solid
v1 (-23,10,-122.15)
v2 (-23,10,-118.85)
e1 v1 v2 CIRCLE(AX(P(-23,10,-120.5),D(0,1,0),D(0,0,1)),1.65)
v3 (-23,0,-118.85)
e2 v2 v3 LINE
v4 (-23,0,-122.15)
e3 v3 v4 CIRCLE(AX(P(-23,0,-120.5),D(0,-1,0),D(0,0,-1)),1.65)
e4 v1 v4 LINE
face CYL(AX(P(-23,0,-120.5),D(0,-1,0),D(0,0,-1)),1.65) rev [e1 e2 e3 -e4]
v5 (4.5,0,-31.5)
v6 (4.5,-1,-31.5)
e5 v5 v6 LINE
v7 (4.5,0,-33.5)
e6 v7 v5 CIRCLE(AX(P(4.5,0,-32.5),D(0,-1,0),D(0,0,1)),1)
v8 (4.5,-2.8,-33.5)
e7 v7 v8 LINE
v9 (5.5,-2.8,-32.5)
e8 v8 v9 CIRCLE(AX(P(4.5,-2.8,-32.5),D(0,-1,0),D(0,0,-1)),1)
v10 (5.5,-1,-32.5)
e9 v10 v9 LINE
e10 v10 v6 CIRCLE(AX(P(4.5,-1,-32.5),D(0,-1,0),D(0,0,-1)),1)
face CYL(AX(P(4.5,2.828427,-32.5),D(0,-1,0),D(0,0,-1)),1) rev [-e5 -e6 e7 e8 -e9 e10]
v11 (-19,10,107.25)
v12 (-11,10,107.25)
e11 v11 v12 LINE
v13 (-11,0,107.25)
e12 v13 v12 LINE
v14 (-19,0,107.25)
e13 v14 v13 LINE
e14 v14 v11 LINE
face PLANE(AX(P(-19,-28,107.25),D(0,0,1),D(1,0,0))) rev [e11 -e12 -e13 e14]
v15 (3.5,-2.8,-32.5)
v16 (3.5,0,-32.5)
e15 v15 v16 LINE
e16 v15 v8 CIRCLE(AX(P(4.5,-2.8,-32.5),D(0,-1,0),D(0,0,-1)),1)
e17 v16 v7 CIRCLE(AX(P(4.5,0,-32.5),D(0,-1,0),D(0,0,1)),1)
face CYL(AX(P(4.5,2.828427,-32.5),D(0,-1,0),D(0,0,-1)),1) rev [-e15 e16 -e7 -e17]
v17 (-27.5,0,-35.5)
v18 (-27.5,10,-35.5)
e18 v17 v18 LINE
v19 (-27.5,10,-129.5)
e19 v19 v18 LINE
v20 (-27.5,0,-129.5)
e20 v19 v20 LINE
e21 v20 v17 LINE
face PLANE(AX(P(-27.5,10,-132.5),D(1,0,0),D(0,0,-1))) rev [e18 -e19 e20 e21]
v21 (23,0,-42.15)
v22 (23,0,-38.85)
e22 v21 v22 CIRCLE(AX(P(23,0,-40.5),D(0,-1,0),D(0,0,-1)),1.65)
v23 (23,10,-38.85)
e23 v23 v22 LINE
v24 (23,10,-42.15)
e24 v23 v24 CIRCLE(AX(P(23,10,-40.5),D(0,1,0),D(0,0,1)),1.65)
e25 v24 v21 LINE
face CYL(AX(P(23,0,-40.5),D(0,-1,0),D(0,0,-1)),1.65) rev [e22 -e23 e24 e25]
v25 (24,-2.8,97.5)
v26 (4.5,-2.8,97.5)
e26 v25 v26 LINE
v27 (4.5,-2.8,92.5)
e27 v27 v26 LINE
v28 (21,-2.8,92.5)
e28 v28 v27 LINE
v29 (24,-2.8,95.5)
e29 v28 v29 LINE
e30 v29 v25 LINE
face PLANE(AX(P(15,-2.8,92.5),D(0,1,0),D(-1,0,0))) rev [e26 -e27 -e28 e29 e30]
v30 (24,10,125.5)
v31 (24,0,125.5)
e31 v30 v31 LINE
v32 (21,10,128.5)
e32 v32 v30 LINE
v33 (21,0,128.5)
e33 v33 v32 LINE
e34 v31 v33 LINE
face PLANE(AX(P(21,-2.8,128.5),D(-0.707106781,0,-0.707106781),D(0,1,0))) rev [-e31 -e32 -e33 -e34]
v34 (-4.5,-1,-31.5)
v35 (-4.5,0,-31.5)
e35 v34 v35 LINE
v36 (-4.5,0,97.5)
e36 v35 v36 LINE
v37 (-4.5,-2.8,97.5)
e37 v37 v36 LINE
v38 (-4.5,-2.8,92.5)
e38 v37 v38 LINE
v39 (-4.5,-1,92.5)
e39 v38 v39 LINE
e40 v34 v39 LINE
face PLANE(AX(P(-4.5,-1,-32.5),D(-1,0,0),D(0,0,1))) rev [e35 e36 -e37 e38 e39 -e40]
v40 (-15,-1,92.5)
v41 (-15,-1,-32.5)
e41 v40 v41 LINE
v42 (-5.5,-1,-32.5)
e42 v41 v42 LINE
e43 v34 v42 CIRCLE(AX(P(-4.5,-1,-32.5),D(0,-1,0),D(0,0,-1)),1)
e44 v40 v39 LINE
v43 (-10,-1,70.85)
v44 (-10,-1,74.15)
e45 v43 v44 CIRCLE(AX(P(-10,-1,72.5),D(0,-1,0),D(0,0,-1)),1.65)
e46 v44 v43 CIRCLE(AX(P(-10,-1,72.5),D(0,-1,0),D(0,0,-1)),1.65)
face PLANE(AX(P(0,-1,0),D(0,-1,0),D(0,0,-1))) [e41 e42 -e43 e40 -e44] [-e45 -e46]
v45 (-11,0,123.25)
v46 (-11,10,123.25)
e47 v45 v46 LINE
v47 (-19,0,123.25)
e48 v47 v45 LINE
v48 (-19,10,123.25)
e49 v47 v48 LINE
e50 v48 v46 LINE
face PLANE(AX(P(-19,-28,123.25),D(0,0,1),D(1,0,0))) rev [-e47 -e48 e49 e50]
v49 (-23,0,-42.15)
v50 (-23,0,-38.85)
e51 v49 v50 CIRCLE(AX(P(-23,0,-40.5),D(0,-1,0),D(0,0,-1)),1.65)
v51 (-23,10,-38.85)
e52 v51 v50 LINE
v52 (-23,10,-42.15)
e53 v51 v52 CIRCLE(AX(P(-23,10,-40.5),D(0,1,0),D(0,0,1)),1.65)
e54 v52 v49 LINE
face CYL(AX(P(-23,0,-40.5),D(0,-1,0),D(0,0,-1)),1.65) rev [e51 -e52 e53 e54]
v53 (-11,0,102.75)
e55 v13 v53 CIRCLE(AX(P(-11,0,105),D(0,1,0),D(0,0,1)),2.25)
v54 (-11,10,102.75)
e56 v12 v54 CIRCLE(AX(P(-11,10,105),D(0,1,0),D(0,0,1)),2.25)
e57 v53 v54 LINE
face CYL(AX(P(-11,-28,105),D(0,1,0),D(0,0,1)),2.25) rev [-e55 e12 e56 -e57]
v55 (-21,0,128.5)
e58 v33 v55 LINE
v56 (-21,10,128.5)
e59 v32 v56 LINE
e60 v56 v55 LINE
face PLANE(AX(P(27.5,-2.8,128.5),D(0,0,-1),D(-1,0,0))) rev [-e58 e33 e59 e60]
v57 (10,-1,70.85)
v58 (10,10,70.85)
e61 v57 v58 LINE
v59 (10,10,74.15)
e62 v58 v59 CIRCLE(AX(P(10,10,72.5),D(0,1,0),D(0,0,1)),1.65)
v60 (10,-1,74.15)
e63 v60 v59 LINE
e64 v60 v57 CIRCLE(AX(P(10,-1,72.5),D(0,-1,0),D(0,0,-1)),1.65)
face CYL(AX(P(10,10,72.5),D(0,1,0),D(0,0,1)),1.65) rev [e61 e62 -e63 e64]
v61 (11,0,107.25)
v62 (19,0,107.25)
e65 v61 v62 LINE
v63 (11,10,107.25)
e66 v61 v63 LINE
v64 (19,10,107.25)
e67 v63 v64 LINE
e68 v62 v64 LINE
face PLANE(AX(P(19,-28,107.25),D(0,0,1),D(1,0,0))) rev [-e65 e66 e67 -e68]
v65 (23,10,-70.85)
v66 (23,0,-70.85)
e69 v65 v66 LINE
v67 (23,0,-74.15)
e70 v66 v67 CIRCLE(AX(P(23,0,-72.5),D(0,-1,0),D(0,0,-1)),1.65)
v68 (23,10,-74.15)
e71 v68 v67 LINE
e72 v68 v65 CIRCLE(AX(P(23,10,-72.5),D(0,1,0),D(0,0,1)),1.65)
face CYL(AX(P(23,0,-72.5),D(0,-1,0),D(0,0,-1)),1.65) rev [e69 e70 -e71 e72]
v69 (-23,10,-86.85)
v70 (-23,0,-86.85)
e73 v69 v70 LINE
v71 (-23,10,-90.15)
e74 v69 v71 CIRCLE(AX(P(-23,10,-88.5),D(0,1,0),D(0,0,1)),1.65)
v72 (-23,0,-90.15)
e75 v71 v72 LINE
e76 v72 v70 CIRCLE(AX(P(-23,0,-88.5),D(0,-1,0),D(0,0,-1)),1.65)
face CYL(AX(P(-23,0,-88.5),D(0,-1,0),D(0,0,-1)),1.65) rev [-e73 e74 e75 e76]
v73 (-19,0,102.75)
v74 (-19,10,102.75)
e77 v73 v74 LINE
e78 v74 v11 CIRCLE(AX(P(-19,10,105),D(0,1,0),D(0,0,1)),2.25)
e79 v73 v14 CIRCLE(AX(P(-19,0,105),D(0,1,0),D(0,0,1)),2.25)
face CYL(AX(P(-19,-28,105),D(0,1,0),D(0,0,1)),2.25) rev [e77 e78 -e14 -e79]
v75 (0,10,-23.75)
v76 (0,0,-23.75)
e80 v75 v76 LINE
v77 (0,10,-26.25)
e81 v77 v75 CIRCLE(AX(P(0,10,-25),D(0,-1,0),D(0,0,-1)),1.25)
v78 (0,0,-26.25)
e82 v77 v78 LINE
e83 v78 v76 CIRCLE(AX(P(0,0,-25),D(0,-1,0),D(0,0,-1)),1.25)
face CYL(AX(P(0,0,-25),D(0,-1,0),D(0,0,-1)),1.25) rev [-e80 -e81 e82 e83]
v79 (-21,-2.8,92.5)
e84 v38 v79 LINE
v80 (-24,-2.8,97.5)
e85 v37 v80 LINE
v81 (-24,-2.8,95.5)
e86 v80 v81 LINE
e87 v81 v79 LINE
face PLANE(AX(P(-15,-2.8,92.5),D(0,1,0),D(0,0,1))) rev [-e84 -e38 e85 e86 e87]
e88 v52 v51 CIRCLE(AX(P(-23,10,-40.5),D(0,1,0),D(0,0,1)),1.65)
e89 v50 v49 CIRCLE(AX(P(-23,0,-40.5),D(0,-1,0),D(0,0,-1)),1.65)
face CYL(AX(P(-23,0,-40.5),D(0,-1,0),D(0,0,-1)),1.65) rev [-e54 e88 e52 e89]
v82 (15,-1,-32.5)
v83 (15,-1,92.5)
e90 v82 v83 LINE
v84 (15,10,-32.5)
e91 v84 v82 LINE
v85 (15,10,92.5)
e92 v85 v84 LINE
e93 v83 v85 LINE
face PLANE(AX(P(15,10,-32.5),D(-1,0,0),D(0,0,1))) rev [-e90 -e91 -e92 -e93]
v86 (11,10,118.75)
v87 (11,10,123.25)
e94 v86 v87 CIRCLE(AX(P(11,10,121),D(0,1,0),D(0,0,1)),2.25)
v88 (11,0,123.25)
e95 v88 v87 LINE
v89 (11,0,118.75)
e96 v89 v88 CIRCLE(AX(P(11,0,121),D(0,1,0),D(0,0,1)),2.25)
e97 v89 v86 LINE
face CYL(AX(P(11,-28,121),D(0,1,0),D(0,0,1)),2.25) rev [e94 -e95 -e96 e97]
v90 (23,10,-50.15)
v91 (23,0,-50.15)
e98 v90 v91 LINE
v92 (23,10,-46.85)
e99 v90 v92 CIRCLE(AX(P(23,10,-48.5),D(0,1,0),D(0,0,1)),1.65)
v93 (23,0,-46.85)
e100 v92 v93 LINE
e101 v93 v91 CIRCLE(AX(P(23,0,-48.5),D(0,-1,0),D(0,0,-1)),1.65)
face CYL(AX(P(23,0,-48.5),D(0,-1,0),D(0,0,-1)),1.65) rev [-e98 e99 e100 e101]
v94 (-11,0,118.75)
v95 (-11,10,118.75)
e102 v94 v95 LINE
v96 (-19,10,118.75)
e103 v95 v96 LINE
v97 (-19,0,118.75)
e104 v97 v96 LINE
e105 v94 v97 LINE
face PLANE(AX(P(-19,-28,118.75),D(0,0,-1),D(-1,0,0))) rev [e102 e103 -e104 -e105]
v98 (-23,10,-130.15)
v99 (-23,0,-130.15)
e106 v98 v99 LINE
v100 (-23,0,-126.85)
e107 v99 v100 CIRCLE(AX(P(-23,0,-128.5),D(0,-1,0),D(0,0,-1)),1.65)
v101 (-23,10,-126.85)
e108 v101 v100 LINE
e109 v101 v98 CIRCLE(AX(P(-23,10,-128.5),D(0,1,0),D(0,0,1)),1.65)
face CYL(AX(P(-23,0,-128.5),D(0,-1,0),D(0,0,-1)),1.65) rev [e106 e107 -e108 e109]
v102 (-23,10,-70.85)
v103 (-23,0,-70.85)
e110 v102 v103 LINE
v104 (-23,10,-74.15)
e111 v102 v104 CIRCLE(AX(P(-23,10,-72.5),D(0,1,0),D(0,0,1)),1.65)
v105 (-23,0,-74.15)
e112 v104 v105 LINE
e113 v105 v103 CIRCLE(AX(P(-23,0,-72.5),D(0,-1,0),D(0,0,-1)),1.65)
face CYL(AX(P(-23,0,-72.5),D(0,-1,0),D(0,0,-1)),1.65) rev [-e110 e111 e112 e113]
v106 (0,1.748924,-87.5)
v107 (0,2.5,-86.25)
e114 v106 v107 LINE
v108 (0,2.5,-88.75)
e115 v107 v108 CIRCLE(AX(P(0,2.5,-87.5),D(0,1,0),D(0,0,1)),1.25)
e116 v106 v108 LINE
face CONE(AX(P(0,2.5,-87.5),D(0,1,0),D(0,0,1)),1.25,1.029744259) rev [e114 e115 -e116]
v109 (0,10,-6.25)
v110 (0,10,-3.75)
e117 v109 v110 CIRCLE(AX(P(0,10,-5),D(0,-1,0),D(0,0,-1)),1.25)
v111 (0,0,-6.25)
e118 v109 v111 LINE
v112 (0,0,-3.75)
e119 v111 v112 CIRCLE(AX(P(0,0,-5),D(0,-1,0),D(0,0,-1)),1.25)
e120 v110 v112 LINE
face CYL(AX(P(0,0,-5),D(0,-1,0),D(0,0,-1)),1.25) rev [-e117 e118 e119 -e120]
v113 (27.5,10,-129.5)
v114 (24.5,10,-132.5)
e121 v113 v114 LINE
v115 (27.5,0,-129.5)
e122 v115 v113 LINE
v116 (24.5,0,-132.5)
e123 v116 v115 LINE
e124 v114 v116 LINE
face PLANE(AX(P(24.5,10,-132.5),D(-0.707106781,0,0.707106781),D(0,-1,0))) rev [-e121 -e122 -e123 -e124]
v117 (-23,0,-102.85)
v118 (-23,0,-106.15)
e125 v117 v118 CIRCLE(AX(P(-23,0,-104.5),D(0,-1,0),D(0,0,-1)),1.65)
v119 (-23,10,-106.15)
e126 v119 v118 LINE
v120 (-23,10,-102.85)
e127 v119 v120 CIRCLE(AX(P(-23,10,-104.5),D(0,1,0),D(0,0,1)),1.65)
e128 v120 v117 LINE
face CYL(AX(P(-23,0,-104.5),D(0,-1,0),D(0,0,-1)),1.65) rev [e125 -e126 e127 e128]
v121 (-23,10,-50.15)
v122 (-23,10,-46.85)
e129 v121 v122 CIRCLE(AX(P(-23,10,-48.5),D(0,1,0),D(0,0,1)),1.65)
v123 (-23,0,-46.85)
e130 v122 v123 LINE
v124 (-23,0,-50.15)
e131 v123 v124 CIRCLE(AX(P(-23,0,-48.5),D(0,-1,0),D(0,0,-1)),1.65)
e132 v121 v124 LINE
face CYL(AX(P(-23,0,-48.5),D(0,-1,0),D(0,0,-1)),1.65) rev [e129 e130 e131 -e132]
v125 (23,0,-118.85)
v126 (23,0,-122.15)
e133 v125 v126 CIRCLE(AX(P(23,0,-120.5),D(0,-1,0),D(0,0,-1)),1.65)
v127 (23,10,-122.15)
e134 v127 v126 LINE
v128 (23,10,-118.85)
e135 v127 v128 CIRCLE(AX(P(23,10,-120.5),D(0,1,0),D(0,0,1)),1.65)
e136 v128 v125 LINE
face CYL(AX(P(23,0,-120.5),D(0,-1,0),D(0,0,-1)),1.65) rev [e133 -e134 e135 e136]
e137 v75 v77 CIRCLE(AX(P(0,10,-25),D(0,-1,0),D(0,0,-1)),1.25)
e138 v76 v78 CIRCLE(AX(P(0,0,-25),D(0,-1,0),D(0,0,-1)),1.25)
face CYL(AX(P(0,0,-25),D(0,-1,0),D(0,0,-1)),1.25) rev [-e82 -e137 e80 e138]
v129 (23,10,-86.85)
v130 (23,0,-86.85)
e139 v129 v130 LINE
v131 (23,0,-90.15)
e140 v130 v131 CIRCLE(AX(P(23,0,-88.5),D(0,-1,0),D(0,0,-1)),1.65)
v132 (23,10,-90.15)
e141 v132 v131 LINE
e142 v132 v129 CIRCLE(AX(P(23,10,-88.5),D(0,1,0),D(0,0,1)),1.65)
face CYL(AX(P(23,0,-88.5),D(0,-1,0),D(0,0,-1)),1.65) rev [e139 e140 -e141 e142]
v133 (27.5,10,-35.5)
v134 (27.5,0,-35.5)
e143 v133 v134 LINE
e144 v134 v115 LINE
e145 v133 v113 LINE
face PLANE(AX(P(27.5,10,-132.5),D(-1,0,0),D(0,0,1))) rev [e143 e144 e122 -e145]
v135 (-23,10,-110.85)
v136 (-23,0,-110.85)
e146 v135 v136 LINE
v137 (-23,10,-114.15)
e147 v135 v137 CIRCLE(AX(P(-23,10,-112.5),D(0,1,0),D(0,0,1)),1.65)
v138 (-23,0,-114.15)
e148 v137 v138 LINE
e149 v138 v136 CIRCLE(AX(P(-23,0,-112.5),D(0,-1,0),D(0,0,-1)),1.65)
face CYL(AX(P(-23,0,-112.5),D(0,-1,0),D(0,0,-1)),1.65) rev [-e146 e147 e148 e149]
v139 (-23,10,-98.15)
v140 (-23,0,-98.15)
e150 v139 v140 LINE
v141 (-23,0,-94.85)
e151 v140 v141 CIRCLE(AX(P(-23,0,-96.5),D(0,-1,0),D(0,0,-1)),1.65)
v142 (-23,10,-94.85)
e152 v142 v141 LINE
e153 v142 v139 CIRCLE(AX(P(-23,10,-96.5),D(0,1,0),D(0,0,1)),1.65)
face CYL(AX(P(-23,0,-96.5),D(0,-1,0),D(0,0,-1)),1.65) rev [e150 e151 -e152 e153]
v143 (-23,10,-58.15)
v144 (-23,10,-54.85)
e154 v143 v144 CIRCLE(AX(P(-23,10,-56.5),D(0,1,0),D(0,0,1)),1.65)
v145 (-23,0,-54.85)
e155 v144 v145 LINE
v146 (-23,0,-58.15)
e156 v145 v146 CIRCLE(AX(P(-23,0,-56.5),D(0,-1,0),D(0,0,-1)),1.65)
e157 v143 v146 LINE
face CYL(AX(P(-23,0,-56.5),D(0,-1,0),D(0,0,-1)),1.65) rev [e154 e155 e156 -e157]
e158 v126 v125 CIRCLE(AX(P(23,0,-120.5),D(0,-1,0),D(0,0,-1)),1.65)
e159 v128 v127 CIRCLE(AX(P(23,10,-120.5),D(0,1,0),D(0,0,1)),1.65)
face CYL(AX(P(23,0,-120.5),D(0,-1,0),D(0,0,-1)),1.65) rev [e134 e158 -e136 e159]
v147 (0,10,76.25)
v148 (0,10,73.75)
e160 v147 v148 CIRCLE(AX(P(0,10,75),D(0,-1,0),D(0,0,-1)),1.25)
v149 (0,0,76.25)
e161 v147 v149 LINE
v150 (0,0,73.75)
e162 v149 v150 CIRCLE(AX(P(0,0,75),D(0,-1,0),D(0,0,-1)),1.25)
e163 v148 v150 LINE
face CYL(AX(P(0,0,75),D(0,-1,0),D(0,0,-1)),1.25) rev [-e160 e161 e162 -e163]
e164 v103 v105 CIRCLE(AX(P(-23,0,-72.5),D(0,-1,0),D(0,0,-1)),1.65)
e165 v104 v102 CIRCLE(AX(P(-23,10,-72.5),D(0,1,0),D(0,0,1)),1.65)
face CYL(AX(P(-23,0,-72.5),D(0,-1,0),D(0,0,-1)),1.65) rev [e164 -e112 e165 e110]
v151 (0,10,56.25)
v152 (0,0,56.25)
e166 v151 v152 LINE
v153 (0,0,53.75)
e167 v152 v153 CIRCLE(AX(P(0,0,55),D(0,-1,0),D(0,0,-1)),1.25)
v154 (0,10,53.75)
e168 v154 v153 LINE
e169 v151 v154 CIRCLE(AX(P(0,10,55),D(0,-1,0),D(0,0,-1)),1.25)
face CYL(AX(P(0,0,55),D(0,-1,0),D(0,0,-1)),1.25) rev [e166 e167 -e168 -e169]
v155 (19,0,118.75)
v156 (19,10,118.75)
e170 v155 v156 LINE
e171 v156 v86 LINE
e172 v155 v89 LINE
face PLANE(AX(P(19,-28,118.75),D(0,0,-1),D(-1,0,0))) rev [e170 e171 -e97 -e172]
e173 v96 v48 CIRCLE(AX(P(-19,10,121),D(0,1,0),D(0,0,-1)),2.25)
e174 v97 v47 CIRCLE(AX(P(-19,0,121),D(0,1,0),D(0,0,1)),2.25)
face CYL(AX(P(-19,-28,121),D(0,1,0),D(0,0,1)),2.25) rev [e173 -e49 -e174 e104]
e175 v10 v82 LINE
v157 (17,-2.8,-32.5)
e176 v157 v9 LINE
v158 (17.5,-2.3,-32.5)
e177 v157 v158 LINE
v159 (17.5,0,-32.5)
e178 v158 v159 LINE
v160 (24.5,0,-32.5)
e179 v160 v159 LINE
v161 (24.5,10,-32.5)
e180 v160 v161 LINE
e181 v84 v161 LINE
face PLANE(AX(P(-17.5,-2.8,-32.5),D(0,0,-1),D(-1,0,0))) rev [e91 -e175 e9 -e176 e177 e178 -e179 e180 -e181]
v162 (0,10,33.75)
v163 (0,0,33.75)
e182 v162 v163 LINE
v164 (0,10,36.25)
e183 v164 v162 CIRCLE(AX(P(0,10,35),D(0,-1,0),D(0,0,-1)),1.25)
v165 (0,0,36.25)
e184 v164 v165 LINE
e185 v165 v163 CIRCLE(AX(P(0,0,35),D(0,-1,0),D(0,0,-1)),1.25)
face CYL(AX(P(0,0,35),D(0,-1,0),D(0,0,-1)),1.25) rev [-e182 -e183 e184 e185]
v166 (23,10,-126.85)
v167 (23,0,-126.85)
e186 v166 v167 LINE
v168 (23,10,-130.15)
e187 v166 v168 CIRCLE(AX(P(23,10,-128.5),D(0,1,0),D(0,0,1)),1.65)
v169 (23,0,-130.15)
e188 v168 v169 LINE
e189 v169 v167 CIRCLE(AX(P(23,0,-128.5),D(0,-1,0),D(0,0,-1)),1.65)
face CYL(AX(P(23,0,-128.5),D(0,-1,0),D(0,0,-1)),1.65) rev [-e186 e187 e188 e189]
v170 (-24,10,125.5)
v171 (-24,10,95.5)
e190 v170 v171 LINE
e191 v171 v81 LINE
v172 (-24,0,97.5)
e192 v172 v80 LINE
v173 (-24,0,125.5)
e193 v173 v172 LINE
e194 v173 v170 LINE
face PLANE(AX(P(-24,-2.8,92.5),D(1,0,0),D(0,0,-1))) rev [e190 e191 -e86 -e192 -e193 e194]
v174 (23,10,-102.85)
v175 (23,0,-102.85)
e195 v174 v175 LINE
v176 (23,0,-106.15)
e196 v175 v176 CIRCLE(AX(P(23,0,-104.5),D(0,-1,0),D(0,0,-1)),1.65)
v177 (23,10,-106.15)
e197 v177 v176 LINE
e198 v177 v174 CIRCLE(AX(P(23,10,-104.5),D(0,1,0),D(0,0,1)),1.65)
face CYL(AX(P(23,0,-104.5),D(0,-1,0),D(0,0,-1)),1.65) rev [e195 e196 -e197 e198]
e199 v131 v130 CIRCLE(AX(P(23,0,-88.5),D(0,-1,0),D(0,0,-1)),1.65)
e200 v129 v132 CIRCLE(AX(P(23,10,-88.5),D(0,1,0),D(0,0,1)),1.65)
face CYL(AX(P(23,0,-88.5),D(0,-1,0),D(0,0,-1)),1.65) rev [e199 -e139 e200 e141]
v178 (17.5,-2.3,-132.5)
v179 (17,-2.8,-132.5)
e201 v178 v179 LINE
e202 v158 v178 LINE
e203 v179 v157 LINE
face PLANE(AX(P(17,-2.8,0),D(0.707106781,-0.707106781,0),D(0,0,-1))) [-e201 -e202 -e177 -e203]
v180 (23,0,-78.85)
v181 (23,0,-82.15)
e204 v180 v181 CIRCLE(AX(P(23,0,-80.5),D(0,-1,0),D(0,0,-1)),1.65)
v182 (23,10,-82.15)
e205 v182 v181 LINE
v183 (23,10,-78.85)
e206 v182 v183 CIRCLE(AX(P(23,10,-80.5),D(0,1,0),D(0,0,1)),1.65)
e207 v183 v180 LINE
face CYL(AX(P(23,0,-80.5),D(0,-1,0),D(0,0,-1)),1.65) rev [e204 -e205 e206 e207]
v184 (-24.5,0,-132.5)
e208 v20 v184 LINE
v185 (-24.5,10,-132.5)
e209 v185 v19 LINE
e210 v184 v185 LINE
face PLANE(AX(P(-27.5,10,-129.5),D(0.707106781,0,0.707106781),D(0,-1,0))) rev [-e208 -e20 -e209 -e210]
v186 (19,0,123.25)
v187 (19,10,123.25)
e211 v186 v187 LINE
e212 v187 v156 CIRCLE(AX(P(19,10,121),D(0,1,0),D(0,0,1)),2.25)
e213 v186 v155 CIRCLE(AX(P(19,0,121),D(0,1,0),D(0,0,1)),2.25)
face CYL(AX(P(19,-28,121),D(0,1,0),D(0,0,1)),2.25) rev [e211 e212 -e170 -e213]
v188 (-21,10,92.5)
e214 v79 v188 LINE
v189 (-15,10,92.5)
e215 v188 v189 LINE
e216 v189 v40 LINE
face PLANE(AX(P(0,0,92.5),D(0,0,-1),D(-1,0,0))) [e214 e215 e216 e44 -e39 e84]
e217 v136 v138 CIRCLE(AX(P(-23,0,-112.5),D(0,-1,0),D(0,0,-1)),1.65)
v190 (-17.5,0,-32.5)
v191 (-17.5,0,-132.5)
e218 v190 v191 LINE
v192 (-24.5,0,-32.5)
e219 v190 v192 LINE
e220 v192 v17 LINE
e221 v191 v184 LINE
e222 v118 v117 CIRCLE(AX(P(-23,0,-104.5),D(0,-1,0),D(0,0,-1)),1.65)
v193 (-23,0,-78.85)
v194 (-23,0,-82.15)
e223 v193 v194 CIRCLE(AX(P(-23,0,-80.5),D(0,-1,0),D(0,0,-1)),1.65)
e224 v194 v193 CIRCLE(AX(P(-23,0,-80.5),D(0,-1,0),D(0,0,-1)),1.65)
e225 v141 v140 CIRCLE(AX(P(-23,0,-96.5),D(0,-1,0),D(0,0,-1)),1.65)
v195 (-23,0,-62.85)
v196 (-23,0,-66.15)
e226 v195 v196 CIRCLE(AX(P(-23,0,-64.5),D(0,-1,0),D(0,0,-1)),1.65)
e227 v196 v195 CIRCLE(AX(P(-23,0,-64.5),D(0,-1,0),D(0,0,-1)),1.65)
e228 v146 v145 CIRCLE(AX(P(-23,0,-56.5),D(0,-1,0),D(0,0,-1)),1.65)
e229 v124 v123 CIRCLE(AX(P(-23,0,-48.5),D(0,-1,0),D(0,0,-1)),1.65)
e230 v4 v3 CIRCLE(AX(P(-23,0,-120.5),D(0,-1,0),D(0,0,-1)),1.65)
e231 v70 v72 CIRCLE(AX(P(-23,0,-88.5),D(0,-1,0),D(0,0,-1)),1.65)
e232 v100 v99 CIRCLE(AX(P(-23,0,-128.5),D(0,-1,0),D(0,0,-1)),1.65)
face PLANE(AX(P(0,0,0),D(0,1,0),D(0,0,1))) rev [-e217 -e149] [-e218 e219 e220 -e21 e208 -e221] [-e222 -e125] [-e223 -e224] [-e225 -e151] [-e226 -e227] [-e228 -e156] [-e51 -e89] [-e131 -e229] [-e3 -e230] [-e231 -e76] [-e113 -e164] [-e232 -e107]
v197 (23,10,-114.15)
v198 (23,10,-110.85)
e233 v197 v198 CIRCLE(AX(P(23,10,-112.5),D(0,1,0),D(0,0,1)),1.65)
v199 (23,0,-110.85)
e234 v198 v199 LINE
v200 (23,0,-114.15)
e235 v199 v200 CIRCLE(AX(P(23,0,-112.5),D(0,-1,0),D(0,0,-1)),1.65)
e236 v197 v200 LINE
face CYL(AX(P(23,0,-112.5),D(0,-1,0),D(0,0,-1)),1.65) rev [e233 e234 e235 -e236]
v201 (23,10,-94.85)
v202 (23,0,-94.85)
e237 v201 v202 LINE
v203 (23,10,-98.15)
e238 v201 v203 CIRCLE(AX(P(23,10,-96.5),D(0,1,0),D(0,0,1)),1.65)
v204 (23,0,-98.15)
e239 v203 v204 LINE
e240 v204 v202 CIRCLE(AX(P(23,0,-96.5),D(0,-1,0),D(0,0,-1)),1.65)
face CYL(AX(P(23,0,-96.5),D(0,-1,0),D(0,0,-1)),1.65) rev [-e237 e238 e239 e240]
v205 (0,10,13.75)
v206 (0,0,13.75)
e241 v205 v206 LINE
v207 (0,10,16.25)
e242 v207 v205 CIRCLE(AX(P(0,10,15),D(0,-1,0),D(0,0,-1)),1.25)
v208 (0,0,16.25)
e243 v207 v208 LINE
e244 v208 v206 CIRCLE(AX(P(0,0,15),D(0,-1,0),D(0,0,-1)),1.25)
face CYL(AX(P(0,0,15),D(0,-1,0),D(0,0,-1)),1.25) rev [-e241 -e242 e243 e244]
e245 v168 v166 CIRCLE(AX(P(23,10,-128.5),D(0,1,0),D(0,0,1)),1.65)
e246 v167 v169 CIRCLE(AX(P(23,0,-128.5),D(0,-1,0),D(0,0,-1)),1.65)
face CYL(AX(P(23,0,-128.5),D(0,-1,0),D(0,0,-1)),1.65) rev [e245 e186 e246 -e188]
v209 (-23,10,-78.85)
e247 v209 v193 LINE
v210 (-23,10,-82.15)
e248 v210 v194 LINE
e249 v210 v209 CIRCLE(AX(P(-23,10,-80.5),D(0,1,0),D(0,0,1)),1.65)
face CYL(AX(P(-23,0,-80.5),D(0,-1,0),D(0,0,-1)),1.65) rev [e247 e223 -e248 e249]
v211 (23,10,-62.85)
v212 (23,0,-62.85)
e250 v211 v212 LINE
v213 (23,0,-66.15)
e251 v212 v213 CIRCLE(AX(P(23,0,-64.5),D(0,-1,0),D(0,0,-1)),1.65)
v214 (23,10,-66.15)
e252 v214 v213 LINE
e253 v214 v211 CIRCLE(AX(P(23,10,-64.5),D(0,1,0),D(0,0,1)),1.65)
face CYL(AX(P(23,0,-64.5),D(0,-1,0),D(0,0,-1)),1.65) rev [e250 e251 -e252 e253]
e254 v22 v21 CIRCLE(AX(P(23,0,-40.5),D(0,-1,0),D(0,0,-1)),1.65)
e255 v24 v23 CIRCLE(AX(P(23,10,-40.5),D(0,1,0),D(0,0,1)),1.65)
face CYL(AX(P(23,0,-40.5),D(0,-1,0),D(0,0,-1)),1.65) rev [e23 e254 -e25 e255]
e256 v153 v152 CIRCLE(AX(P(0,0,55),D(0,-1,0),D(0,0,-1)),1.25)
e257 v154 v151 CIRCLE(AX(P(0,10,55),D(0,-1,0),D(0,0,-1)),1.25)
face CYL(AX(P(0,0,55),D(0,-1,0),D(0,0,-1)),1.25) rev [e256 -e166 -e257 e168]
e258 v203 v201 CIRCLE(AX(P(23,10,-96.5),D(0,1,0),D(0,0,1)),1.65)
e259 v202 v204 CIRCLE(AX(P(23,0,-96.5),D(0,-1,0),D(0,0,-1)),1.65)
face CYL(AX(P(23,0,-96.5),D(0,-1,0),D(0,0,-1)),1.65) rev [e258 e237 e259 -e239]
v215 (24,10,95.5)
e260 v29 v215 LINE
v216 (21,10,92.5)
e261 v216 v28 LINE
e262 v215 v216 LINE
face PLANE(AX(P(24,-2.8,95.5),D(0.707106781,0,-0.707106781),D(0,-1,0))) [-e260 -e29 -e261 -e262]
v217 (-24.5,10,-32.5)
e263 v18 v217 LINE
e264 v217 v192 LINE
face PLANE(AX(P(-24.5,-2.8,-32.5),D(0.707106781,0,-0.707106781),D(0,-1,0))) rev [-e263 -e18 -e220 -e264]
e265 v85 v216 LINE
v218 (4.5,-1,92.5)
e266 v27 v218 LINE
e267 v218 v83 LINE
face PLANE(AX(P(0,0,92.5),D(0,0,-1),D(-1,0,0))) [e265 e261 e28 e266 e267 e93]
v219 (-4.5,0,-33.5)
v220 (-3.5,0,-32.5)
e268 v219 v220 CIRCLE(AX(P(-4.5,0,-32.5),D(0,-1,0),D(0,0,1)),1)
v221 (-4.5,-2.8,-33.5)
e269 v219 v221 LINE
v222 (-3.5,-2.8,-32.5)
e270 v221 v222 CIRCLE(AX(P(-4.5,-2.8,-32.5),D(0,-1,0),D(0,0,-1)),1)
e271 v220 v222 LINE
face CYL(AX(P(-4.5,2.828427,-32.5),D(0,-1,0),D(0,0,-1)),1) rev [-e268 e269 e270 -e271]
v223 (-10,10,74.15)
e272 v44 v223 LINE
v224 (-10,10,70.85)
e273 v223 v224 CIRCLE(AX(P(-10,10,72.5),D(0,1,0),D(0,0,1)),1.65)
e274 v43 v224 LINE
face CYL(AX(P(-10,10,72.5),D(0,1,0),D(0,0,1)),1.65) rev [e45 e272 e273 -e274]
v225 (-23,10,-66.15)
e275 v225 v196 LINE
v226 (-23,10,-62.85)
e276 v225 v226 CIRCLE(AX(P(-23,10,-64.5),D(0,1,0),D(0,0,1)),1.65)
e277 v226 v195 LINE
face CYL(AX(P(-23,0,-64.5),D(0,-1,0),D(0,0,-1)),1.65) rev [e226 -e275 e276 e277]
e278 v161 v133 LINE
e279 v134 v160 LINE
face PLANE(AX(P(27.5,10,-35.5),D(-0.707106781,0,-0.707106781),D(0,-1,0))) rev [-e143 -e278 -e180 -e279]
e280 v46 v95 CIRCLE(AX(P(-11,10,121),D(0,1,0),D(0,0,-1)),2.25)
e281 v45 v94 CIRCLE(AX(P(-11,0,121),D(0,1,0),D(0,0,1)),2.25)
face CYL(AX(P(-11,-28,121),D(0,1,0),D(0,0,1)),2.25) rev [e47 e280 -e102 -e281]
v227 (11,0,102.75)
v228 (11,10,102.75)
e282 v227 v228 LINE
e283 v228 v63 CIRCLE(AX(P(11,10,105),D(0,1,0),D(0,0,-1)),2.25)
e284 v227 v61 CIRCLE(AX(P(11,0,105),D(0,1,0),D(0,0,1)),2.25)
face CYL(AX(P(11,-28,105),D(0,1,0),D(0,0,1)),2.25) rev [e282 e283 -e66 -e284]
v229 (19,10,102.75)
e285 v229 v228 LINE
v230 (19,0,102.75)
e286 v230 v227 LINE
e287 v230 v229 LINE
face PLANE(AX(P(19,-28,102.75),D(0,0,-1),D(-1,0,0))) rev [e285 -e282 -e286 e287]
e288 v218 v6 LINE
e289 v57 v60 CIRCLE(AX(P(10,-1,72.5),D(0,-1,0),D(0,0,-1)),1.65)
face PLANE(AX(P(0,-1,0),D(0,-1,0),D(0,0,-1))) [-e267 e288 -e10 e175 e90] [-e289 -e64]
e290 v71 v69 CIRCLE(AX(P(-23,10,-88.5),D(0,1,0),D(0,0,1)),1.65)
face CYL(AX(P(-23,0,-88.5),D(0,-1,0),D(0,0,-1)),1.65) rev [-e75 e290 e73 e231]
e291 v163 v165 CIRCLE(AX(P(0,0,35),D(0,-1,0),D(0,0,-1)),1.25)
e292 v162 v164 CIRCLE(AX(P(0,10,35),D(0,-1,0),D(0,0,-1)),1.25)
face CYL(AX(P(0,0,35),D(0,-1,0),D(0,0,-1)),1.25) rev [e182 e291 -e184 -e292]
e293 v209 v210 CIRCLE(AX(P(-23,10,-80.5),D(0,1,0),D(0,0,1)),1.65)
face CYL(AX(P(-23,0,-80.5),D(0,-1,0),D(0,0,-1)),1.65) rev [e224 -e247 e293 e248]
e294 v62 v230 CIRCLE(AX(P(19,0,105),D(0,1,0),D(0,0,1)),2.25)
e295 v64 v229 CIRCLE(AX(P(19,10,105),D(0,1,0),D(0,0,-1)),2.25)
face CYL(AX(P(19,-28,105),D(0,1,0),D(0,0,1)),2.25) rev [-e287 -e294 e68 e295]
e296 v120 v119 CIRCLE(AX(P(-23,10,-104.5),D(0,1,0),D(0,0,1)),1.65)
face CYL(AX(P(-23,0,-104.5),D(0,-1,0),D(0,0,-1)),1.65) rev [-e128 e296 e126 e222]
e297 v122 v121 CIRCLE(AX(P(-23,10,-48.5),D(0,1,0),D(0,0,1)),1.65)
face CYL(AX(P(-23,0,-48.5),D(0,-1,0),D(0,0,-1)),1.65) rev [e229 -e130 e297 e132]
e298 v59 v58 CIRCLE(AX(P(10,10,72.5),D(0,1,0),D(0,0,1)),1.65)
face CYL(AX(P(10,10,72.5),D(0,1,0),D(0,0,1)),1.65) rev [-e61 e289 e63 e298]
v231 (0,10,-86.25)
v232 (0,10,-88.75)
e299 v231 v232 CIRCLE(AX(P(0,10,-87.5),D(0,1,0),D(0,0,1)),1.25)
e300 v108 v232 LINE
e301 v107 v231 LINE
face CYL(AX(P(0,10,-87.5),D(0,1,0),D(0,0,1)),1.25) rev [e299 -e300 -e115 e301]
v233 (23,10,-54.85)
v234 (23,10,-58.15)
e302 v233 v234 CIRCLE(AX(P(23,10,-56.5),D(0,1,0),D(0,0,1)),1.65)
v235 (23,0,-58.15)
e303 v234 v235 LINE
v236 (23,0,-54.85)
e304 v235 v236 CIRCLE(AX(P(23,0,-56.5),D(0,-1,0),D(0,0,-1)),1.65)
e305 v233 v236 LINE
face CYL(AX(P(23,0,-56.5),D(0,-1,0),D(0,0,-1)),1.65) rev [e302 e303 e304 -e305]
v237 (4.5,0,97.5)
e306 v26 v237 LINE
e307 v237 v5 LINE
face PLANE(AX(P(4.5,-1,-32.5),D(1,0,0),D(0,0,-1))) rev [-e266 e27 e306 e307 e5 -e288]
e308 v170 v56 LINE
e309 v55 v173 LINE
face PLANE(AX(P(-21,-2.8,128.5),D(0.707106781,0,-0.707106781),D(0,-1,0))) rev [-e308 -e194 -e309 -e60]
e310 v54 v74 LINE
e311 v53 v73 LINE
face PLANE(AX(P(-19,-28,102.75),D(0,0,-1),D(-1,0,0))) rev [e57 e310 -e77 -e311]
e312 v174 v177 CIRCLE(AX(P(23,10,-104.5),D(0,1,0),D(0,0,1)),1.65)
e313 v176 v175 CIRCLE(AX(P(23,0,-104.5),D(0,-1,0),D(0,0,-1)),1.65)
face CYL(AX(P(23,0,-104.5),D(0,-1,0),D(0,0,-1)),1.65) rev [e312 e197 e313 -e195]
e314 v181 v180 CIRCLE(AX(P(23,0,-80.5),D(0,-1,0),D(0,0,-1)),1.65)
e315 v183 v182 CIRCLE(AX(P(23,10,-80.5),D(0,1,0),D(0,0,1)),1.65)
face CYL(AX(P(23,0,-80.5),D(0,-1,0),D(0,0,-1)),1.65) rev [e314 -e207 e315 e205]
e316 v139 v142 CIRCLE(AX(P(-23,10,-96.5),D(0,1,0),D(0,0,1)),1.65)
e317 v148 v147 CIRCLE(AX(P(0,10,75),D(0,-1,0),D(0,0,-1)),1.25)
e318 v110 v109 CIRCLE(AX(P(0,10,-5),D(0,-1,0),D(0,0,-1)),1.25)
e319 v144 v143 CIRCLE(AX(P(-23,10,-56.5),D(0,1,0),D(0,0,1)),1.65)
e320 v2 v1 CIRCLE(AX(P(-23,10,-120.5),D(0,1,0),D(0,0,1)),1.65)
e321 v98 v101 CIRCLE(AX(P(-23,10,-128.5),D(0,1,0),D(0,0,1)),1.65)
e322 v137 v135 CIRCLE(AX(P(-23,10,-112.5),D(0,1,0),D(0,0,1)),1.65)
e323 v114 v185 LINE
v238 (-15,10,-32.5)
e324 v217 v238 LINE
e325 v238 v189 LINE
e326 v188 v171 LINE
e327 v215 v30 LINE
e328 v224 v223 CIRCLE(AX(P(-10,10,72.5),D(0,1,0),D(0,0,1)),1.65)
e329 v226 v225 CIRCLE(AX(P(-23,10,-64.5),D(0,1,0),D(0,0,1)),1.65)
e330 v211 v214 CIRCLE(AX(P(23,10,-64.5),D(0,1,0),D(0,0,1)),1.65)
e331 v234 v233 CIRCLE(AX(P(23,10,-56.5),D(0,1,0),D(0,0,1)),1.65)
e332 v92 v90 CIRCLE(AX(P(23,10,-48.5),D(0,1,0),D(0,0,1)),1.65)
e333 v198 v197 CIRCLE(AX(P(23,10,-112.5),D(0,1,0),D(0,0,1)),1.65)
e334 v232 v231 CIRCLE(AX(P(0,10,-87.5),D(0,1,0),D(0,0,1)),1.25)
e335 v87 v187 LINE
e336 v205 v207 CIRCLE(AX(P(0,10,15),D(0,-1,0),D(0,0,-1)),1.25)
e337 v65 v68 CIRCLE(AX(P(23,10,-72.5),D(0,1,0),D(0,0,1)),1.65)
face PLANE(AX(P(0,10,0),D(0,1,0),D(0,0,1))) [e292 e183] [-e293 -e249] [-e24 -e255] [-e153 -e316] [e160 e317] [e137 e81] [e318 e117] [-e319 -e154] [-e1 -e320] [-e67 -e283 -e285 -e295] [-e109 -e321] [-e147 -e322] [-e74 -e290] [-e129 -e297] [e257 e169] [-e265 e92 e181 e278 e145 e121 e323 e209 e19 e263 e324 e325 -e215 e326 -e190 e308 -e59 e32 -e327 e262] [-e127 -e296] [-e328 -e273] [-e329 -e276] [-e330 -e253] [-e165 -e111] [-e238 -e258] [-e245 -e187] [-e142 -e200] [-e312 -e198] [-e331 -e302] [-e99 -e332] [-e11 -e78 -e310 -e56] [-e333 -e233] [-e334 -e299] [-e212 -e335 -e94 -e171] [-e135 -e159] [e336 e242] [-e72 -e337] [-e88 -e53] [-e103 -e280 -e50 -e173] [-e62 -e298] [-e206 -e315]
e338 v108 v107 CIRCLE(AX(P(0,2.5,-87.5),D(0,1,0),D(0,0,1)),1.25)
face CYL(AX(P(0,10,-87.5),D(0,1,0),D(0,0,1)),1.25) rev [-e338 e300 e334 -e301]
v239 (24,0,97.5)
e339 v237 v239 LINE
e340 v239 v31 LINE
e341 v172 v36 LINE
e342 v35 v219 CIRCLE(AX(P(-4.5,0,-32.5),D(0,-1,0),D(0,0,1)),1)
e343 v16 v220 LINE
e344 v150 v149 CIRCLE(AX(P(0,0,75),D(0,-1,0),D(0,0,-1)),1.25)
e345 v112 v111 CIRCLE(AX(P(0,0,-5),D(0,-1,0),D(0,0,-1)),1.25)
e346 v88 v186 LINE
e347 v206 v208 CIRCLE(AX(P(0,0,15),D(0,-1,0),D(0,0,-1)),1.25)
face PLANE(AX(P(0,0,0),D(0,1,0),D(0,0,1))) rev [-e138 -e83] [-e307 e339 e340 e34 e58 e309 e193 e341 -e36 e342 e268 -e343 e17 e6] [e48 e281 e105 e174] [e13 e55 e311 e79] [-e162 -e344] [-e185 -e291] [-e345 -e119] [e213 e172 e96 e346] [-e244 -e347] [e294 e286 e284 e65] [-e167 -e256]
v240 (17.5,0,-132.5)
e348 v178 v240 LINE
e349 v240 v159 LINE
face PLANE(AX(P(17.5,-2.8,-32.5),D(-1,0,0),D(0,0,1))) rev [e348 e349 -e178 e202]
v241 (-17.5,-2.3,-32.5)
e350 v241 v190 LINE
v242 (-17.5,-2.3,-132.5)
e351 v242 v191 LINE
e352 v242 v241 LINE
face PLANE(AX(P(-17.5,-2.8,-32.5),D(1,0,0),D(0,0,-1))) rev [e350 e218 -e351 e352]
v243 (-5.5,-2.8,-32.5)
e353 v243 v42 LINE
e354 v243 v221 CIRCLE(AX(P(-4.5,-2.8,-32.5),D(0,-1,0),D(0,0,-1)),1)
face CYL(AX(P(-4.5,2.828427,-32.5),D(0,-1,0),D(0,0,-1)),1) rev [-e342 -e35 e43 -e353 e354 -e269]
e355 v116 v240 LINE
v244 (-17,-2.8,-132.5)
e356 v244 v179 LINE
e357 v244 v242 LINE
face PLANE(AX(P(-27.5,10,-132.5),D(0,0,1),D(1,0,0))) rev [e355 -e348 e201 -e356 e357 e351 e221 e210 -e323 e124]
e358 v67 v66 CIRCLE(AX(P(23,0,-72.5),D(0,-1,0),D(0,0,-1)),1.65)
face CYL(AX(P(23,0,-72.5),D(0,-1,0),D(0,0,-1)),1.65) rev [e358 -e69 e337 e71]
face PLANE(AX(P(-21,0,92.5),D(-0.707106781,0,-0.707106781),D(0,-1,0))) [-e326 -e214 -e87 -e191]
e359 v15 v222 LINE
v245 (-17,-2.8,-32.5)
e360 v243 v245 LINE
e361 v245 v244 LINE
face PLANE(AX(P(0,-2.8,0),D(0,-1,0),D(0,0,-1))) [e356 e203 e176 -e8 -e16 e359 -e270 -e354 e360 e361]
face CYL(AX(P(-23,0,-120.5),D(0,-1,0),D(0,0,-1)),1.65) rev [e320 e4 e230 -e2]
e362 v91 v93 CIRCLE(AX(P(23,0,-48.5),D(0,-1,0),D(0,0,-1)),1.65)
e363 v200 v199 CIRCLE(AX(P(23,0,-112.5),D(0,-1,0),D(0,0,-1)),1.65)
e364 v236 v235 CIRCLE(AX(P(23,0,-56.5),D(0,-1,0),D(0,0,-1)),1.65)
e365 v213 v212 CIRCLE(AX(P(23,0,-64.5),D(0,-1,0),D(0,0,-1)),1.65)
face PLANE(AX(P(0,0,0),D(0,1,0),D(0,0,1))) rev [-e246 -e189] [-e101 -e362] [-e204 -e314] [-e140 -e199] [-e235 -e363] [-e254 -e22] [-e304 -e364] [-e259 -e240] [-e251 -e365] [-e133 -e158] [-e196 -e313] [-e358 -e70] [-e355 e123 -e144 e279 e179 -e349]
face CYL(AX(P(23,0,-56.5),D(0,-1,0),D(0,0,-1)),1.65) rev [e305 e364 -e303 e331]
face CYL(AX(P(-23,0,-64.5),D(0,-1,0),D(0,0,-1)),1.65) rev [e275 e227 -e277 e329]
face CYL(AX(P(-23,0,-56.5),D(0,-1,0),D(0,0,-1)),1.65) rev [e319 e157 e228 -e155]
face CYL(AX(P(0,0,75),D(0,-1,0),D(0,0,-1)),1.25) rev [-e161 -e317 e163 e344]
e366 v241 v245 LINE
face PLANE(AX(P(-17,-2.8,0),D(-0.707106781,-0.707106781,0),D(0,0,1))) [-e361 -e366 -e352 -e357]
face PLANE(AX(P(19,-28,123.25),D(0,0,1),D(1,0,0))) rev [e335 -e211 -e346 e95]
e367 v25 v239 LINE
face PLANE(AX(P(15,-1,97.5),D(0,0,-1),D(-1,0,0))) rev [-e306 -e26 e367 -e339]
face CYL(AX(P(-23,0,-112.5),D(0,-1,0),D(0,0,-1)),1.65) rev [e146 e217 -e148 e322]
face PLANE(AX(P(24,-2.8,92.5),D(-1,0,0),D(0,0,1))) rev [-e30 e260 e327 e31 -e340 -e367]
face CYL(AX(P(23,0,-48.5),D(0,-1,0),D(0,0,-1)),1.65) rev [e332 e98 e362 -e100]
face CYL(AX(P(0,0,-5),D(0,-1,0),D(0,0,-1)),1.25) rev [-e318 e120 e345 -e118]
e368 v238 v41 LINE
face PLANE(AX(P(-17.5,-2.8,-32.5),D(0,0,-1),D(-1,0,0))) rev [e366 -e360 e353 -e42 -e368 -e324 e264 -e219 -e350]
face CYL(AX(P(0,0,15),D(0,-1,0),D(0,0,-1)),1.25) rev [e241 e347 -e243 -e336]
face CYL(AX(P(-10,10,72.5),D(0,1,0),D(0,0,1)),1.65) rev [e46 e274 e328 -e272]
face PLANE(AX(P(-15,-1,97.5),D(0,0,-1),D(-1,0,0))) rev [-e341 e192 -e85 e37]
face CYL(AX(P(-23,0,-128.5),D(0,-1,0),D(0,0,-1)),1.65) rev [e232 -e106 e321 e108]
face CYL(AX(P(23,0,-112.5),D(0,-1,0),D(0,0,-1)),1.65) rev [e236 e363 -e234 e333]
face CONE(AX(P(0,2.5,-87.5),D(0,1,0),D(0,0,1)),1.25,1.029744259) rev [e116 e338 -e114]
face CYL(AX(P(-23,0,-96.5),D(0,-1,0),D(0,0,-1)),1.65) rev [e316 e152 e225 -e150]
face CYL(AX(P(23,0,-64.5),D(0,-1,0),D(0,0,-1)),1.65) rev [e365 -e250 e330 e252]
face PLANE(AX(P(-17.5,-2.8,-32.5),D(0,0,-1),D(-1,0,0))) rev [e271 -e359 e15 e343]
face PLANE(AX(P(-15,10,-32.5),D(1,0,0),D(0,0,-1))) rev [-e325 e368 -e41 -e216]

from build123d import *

# Parameters (mm, degrees)
SKETCH1_W             = 55
SKETCH1_H             = 265
BOSS_EXTRUDE1_DEPTH   = 10
SKETCH2_W             = 35
SKETCH2_H             = 100
BOSS_EXTRUDE2_DEPTH   = 2.8
SKETCH4_W             = 12.5
SKETCH4_H             = 130
CUT_EXTRUDE2_DEPTH    = 136.927701371
CUT_EXTRUDE3_DEPTH    = 38
CHAMFER2_SIZE         = 0.5
CHAMFER3_SIZE         = 3
LPATTERN1_COUNT       = 12
LPATTERN1_PITCH       = 8
SKETCH9_W             = 10.5
SKETCH9_H             = 130
BOSS_EXTRUDE3_DEPTH   = 1
SKETCH10_W            = 12.5
SKETCH10_H            = 12.8
BOSS_EXTRUDE4_DEPTH   = 5
CUT_EXTRUDE4_START    = -2.8
SKETCH11_R            = 1
CUT_EXTRUDE4_DEPTH    = 2.8
M3_TAPPED_HOLE1_D     = 2.5
LPATTERN2_COUNT       = 6
LPATTERN2_PITCH       = 20
SKETCH15_W            = 10.5
SKETCH15_H            = 5
BOSS_EXTRUDE5_DEPTH   = 1.8
M4_TAPPED_HOLE2_D     = 3.3
SKETCH20_W            = 55
SKETCH20_H            = 4
CUT_EXTRUDE6_DEPTH    = 136.927701371
SKETCH21_W            = 3.5
SKETCH21_H            = 36
CUT_EXTRUDE7_DEPTH    = 136.927701371
CHAMFER4_SIZE         = 3
M3_TAPPED_HOLE2_D     = 2.5
M3_TAPPED_HOLE2_DEPTH = 7.5
M3_TAPPED_HOLE2_TIP   = 0.751075774


with BuildPart() as part:
    # Sketch1 → Boss-Extrude1 (new body)
    with BuildSketch(Plane(origin=(0, 0, 0), x_dir=(1, 0, 0), z_dir=(0, 1, 0))):
        Rectangle(SKETCH1_W, SKETCH1_H)
    extrude(amount=BOSS_EXTRUDE1_DEPTH)

    # Sketch2 → Boss-Extrude2 (add)
    with BuildSketch(Plane.XZ):
        with Locations((0, -82.5)):
            Rectangle(SKETCH2_W, SKETCH2_H)
    extrude(amount=BOSS_EXTRUDE2_DEPTH)

    # Sketch4 → Cut-Extrude2 (cut, through all)
    with BuildSketch(Plane.XZ.offset(2.8)):
        with Locations((-21.25, 32.5)):
            Rectangle(SKETCH4_W, SKETCH4_H)
        with Locations((21.25, 32.5)):
            Rectangle(SKETCH4_W, SKETCH4_H)
    extrude(amount=-CUT_EXTRUDE2_DEPTH, mode=Mode.SUBTRACT)

    # Sketch5 → Cut-Extrude3 (cut)
    with BuildSketch(Plane(origin=(0, 10, 0), x_dir=(1, 0, 0), z_dir=(0, 1, 0))):
        with BuildLine():
            Line((-19, -123.25), (-11, -123.25))
            ThreePointArc((-11, -123.25), (-8.75, -121), (-11, -118.75))
            Line((-11, -118.75), (-19, -118.75))
            ThreePointArc((-19, -118.75), (-21.25, -121), (-19, -123.25))
        make_face()
        with BuildLine():
            Line((19, -102.75), (11, -102.75))
            ThreePointArc((11, -102.75), (8.75, -105), (11, -107.25))
            Line((11, -107.25), (19, -107.25))
            ThreePointArc((19, -107.25), (21.25, -105), (19, -102.75))
        make_face()
        with BuildLine():
            Line((19, -123.25), (11, -123.25))
            ThreePointArc((11, -123.25), (8.75, -121), (11, -118.75))
            Line((11, -118.75), (19, -118.75))
            ThreePointArc((19, -118.75), (21.25, -121), (19, -123.25))
        make_face()
        with BuildLine():
            Line((-19, -102.75), (-11, -102.75))
            ThreePointArc((-11, -102.75), (-8.75, -105), (-11, -107.25))
            Line((-11, -107.25), (-19, -107.25))
            ThreePointArc((-19, -107.25), (-21.25, -105), (-19, -102.75))
        make_face()
    extrude(amount=-CUT_EXTRUDE3_DEPTH, mode=Mode.SUBTRACT)

    # Chamfer2
    chamfer2_edges = [part.edges().sort_by_distance(p)[0] for p in [
        (17.5, -2.8, -82.5),
        (-17.5, -2.8, -82.5),
    ]]
    chamfer(chamfer2_edges, length=CHAMFER2_SIZE)

    # Chamfer3
    chamfer3_edges = [part.edges().sort_by_distance(p)[0] for p in [
        (-27.5, 5, -132.5),
        (27.5, 5, -132.5),
        (27.5, 5, -32.5),
        (-27.5, 5, -32.5),
    ]]
    chamfer(chamfer3_edges, length=CHAMFER3_SIZE)

    # Sketch7 → M4 Tapped Hole1 (revolve, cut)
    with BuildSketch(Plane(origin=(-23, 0, -128.5), x_dir=(0, 0, -1), z_dir=(1, 0, 0))):
        Polygon((0, 0), (0, 11.091420021), (1.65, 10.1), (1.65, 0), align=None)
    m4_tapped_hole1 = revolve(axis=Axis((-23, -6.35, -128.5), (0, 1, 0)), mode=Mode.SUBTRACT)

    # Mirror1: M4 Tapped Hole1 across plane
    add(m4_tapped_hole1.mirror(Plane(origin=(0, 0, 0), x_dir=(0, 0, 1), z_dir=(1, 0, 0))), mode=Mode.SUBTRACT)

    # LPattern1: M4 Tapped Hole1 ×12
    with Locations(*[(0, 0, i * LPATTERN1_PITCH) for i in range(1, LPATTERN1_COUNT)]):
        add(m4_tapped_hole1, mode=Mode.SUBTRACT)

    # LPattern1 copy 1 sketch → LPattern1 copy 1 (revolve, cut)
    with BuildSketch(Plane(origin=(23, 0, -120.5), x_dir=(0, 0, -1), z_dir=(-1, 0, 0))):
        Polygon((0, 0), (0, -11.091420021), (1.65, -10.1), (1.65, 0), align=None)
    revolve(axis=Axis((23, -6.35, -120.5), (0, -1, 0)), mode=Mode.SUBTRACT)

    # LPattern1 copy 2 sketch → LPattern1 copy 2 (revolve, cut)
    with BuildSketch(Plane(origin=(23, 0, -112.5), x_dir=(0, 0, -1), z_dir=(-1, 0, 0))):
        Polygon((0, 0), (0, -11.091420021), (1.65, -10.1), (1.65, 0), align=None)
    revolve(axis=Axis((23, -6.35, -112.5), (0, -1, 0)), mode=Mode.SUBTRACT)

    # LPattern1 copy 3 sketch → LPattern1 copy 3 (revolve, cut)
    with BuildSketch(Plane(origin=(23, 0, -104.5), x_dir=(0, 0, -1), z_dir=(-1, 0, 0))):
        Polygon((0, 0), (0, -11.091420021), (1.65, -10.1), (1.65, 0), align=None)
    revolve(axis=Axis((23, -6.35, -104.5), (0, -1, 0)), mode=Mode.SUBTRACT)

    # LPattern1 copy 4 sketch → LPattern1 copy 4 (revolve, cut)
    with BuildSketch(Plane(origin=(23, 0, -96.5), x_dir=(0, 0, -1), z_dir=(-1, 0, 0))):
        Polygon((0, 0), (0, -11.091420021), (1.65, -10.1), (1.65, 0), align=None)
    revolve(axis=Axis((23, -6.35, -96.5), (0, -1, 0)), mode=Mode.SUBTRACT)

    # LPattern1 copy 5 sketch → LPattern1 copy 5 (revolve, cut)
    with BuildSketch(Plane(origin=(23, 0, -88.5), x_dir=(0, 0, -1), z_dir=(-1, 0, 0))):
        Polygon((0, 0), (0, -11.091420021), (1.65, -10.1), (1.65, 0), align=None)
    revolve(axis=Axis((23, -6.35, -88.5), (0, -1, 0)), mode=Mode.SUBTRACT)

    # LPattern1 copy 6 sketch → LPattern1 copy 6 (revolve, cut)
    with BuildSketch(Plane(origin=(23, 0, -80.5), x_dir=(0, 0, -1), z_dir=(-1, 0, 0))):
        Polygon((0, 0), (0, -11.091420021), (1.65, -10.1), (1.65, 0), align=None)
    revolve(axis=Axis((23, -6.35, -80.5), (0, -1, 0)), mode=Mode.SUBTRACT)

    # LPattern1 copy 7 sketch → LPattern1 copy 7 (revolve, cut)
    with BuildSketch(Plane(origin=(23, 0, -72.5), x_dir=(0, 0, -1), z_dir=(-1, 0, 0))):
        Polygon((0, 0), (0, -11.091420021), (1.65, -10.1), (1.65, 0), align=None)
    revolve(axis=Axis((23, -6.35, -72.5), (0, -1, 0)), mode=Mode.SUBTRACT)

    # LPattern1 copy 8 sketch → LPattern1 copy 8 (revolve, cut)
    with BuildSketch(Plane(origin=(23, 0, -64.5), x_dir=(0, 0, -1), z_dir=(-1, 0, 0))):
        Polygon((0, 0), (0, -11.091420021), (1.65, -10.1), (1.65, 0), align=None)
    revolve(axis=Axis((23, -6.35, -64.5), (0, -1, 0)), mode=Mode.SUBTRACT)

    # LPattern1 copy 9 sketch → LPattern1 copy 9 (revolve, cut)
    with BuildSketch(Plane(origin=(23, 0, -56.5), x_dir=(0, 0, -1), z_dir=(-1, 0, 0))):
        Polygon((0, 0), (0, -11.091420021), (1.65, -10.1), (1.65, 0), align=None)
    revolve(axis=Axis((23, -6.35, -56.5), (0, -1, 0)), mode=Mode.SUBTRACT)

    # LPattern1 copy 10 sketch → LPattern1 copy 10 (revolve, cut)
    with BuildSketch(Plane(origin=(23, 0, -48.5), x_dir=(0, 0, -1), z_dir=(-1, 0, 0))):
        Polygon((0, 0), (0, -11.091420021), (1.65, -10.1), (1.65, 0), align=None)
    revolve(axis=Axis((23, -6.35, -48.5), (0, -1, 0)), mode=Mode.SUBTRACT)

    # LPattern1 copy 11 sketch → LPattern1 copy 11 (revolve, cut)
    with BuildSketch(Plane(origin=(23, 0, -40.5), x_dir=(0, 0, -1), z_dir=(-1, 0, 0))):
        Polygon((0, 0), (0, -11.091420021), (1.65, -10.1), (1.65, 0), align=None)
    revolve(axis=Axis((23, -6.35, -40.5), (0, -1, 0)), mode=Mode.SUBTRACT)

    # Sketch9 → Boss-Extrude3 (add)
    with BuildSketch(Plane.XZ):
        with Locations((-9.75, 32.5)):
            Rectangle(SKETCH9_W, SKETCH9_H)
        with Locations((9.75, 32.5)):
            Rectangle(SKETCH9_W, SKETCH9_H)
    extrude(amount=BOSS_EXTRUDE3_DEPTH)

    # Sketch10 → Boss-Extrude4 (add)
    with BuildSketch(Plane(origin=(0, 0, 97.5), x_dir=(-1, 0, 0), z_dir=(0, 0, -1))):
        with Locations((21.25, 3.6)):
            Rectangle(SKETCH10_W, SKETCH10_H)
        with Locations((-21.25, 3.6)):
            Rectangle(SKETCH10_W, SKETCH10_H)
    extrude(amount=BOSS_EXTRUDE4_DEPTH)

    # Sketch11 → Cut-Extrude4 (cut)
    with BuildSketch(Plane.XZ.offset(2.8).offset(CUT_EXTRUDE4_START)):
        with Locations((4.5, -32.5)):
            Circle(SKETCH11_R)
        with Locations((-4.5, -32.5)):
            Circle(SKETCH11_R)
    extrude(amount=CUT_EXTRUDE4_DEPTH, mode=Mode.SUBTRACT)

    # M3 Tapped Hole1 (through all)
    with Locations(Plane(origin=(0, 0, 0), x_dir=(-1, 0, 0), z_dir=(0, -1, 0))):
        with Locations((0, 25)):
            m3_tapped_hole1 = Hole(M3_TAPPED_HOLE1_D / 2)

    # LPattern2: M3 Tapped Hole1 ×6
    with Locations(*[(0, 0, i * LPATTERN2_PITCH) for i in range(1, LPATTERN2_COUNT)]):
        add(m3_tapped_hole1, mode=Mode.SUBTRACT)

    # Sketch15 → Boss-Extrude5 (add)
    with BuildSketch(Plane.XZ.offset(1)):
        with Locations((-9.75, 95)):
            Rectangle(SKETCH15_W, SKETCH15_H)
        with Locations((9.75, 95)):
            Rectangle(SKETCH15_W, SKETCH15_H)
    extrude(amount=BOSS_EXTRUDE5_DEPTH)

    # M4 Tapped Hole2 (through all)
    with Locations(Plane(origin=(0, 10, 0), x_dir=(1, 0, 0), z_dir=(0, 1, 0))):
        with Locations((-10, -72.5), (10, -72.5)):
            Hole(M4_TAPPED_HOLE2_D / 2)

    # Sketch20 → Cut-Extrude6 (cut, through all)
    with BuildSketch(Plane(origin=(0, 10, 0), x_dir=(1, 0, 0), z_dir=(0, 1, 0))):
        with Locations((0, -130.5)):
            Rectangle(SKETCH20_W, SKETCH20_H)
    extrude(amount=-CUT_EXTRUDE6_DEPTH, mode=Mode.SUBTRACT)

    # Sketch21 → Cut-Extrude7 (cut, through all)
    with BuildSketch(Plane(origin=(0, 10, 0), x_dir=(1, 0, 0), z_dir=(0, 1, 0))):
        with Locations((-25.75, -110.5)):
            Rectangle(SKETCH21_W, SKETCH21_H)
        with Locations((25.75, -110.5)):
            Rectangle(SKETCH21_W, SKETCH21_H)
    extrude(amount=-CUT_EXTRUDE7_DEPTH, mode=Mode.SUBTRACT)

    # Chamfer4
    chamfer4_edges = [part.edges().sort_by_distance(p)[0] for p in [
        (-24, 5, 128.5),
        (-24, 3.6, 92.5),
        (24, 5, 128.5),
        (24, 3.6, 92.5),
    ]]
    chamfer(chamfer4_edges, length=CHAMFER4_SIZE)

    # M3 Tapped Hole2
    with Locations(Plane(origin=(0, 10, 0), x_dir=(1, 0, 0), z_dir=(0, 1, 0))):
        with Locations((0, 87.5)):
            Hole(M3_TAPPED_HOLE2_D / 2, depth=M3_TAPPED_HOLE2_DEPTH)
            with Locations((0, 0, -(M3_TAPPED_HOLE2_DEPTH + M3_TAPPED_HOLE2_TIP / 2))):  # 118° drill point
                Cone(0, M3_TAPPED_HOLE2_D / 2, M3_TAPPED_HOLE2_TIP, mode=Mode.SUBTRACT)


solid = part.part
